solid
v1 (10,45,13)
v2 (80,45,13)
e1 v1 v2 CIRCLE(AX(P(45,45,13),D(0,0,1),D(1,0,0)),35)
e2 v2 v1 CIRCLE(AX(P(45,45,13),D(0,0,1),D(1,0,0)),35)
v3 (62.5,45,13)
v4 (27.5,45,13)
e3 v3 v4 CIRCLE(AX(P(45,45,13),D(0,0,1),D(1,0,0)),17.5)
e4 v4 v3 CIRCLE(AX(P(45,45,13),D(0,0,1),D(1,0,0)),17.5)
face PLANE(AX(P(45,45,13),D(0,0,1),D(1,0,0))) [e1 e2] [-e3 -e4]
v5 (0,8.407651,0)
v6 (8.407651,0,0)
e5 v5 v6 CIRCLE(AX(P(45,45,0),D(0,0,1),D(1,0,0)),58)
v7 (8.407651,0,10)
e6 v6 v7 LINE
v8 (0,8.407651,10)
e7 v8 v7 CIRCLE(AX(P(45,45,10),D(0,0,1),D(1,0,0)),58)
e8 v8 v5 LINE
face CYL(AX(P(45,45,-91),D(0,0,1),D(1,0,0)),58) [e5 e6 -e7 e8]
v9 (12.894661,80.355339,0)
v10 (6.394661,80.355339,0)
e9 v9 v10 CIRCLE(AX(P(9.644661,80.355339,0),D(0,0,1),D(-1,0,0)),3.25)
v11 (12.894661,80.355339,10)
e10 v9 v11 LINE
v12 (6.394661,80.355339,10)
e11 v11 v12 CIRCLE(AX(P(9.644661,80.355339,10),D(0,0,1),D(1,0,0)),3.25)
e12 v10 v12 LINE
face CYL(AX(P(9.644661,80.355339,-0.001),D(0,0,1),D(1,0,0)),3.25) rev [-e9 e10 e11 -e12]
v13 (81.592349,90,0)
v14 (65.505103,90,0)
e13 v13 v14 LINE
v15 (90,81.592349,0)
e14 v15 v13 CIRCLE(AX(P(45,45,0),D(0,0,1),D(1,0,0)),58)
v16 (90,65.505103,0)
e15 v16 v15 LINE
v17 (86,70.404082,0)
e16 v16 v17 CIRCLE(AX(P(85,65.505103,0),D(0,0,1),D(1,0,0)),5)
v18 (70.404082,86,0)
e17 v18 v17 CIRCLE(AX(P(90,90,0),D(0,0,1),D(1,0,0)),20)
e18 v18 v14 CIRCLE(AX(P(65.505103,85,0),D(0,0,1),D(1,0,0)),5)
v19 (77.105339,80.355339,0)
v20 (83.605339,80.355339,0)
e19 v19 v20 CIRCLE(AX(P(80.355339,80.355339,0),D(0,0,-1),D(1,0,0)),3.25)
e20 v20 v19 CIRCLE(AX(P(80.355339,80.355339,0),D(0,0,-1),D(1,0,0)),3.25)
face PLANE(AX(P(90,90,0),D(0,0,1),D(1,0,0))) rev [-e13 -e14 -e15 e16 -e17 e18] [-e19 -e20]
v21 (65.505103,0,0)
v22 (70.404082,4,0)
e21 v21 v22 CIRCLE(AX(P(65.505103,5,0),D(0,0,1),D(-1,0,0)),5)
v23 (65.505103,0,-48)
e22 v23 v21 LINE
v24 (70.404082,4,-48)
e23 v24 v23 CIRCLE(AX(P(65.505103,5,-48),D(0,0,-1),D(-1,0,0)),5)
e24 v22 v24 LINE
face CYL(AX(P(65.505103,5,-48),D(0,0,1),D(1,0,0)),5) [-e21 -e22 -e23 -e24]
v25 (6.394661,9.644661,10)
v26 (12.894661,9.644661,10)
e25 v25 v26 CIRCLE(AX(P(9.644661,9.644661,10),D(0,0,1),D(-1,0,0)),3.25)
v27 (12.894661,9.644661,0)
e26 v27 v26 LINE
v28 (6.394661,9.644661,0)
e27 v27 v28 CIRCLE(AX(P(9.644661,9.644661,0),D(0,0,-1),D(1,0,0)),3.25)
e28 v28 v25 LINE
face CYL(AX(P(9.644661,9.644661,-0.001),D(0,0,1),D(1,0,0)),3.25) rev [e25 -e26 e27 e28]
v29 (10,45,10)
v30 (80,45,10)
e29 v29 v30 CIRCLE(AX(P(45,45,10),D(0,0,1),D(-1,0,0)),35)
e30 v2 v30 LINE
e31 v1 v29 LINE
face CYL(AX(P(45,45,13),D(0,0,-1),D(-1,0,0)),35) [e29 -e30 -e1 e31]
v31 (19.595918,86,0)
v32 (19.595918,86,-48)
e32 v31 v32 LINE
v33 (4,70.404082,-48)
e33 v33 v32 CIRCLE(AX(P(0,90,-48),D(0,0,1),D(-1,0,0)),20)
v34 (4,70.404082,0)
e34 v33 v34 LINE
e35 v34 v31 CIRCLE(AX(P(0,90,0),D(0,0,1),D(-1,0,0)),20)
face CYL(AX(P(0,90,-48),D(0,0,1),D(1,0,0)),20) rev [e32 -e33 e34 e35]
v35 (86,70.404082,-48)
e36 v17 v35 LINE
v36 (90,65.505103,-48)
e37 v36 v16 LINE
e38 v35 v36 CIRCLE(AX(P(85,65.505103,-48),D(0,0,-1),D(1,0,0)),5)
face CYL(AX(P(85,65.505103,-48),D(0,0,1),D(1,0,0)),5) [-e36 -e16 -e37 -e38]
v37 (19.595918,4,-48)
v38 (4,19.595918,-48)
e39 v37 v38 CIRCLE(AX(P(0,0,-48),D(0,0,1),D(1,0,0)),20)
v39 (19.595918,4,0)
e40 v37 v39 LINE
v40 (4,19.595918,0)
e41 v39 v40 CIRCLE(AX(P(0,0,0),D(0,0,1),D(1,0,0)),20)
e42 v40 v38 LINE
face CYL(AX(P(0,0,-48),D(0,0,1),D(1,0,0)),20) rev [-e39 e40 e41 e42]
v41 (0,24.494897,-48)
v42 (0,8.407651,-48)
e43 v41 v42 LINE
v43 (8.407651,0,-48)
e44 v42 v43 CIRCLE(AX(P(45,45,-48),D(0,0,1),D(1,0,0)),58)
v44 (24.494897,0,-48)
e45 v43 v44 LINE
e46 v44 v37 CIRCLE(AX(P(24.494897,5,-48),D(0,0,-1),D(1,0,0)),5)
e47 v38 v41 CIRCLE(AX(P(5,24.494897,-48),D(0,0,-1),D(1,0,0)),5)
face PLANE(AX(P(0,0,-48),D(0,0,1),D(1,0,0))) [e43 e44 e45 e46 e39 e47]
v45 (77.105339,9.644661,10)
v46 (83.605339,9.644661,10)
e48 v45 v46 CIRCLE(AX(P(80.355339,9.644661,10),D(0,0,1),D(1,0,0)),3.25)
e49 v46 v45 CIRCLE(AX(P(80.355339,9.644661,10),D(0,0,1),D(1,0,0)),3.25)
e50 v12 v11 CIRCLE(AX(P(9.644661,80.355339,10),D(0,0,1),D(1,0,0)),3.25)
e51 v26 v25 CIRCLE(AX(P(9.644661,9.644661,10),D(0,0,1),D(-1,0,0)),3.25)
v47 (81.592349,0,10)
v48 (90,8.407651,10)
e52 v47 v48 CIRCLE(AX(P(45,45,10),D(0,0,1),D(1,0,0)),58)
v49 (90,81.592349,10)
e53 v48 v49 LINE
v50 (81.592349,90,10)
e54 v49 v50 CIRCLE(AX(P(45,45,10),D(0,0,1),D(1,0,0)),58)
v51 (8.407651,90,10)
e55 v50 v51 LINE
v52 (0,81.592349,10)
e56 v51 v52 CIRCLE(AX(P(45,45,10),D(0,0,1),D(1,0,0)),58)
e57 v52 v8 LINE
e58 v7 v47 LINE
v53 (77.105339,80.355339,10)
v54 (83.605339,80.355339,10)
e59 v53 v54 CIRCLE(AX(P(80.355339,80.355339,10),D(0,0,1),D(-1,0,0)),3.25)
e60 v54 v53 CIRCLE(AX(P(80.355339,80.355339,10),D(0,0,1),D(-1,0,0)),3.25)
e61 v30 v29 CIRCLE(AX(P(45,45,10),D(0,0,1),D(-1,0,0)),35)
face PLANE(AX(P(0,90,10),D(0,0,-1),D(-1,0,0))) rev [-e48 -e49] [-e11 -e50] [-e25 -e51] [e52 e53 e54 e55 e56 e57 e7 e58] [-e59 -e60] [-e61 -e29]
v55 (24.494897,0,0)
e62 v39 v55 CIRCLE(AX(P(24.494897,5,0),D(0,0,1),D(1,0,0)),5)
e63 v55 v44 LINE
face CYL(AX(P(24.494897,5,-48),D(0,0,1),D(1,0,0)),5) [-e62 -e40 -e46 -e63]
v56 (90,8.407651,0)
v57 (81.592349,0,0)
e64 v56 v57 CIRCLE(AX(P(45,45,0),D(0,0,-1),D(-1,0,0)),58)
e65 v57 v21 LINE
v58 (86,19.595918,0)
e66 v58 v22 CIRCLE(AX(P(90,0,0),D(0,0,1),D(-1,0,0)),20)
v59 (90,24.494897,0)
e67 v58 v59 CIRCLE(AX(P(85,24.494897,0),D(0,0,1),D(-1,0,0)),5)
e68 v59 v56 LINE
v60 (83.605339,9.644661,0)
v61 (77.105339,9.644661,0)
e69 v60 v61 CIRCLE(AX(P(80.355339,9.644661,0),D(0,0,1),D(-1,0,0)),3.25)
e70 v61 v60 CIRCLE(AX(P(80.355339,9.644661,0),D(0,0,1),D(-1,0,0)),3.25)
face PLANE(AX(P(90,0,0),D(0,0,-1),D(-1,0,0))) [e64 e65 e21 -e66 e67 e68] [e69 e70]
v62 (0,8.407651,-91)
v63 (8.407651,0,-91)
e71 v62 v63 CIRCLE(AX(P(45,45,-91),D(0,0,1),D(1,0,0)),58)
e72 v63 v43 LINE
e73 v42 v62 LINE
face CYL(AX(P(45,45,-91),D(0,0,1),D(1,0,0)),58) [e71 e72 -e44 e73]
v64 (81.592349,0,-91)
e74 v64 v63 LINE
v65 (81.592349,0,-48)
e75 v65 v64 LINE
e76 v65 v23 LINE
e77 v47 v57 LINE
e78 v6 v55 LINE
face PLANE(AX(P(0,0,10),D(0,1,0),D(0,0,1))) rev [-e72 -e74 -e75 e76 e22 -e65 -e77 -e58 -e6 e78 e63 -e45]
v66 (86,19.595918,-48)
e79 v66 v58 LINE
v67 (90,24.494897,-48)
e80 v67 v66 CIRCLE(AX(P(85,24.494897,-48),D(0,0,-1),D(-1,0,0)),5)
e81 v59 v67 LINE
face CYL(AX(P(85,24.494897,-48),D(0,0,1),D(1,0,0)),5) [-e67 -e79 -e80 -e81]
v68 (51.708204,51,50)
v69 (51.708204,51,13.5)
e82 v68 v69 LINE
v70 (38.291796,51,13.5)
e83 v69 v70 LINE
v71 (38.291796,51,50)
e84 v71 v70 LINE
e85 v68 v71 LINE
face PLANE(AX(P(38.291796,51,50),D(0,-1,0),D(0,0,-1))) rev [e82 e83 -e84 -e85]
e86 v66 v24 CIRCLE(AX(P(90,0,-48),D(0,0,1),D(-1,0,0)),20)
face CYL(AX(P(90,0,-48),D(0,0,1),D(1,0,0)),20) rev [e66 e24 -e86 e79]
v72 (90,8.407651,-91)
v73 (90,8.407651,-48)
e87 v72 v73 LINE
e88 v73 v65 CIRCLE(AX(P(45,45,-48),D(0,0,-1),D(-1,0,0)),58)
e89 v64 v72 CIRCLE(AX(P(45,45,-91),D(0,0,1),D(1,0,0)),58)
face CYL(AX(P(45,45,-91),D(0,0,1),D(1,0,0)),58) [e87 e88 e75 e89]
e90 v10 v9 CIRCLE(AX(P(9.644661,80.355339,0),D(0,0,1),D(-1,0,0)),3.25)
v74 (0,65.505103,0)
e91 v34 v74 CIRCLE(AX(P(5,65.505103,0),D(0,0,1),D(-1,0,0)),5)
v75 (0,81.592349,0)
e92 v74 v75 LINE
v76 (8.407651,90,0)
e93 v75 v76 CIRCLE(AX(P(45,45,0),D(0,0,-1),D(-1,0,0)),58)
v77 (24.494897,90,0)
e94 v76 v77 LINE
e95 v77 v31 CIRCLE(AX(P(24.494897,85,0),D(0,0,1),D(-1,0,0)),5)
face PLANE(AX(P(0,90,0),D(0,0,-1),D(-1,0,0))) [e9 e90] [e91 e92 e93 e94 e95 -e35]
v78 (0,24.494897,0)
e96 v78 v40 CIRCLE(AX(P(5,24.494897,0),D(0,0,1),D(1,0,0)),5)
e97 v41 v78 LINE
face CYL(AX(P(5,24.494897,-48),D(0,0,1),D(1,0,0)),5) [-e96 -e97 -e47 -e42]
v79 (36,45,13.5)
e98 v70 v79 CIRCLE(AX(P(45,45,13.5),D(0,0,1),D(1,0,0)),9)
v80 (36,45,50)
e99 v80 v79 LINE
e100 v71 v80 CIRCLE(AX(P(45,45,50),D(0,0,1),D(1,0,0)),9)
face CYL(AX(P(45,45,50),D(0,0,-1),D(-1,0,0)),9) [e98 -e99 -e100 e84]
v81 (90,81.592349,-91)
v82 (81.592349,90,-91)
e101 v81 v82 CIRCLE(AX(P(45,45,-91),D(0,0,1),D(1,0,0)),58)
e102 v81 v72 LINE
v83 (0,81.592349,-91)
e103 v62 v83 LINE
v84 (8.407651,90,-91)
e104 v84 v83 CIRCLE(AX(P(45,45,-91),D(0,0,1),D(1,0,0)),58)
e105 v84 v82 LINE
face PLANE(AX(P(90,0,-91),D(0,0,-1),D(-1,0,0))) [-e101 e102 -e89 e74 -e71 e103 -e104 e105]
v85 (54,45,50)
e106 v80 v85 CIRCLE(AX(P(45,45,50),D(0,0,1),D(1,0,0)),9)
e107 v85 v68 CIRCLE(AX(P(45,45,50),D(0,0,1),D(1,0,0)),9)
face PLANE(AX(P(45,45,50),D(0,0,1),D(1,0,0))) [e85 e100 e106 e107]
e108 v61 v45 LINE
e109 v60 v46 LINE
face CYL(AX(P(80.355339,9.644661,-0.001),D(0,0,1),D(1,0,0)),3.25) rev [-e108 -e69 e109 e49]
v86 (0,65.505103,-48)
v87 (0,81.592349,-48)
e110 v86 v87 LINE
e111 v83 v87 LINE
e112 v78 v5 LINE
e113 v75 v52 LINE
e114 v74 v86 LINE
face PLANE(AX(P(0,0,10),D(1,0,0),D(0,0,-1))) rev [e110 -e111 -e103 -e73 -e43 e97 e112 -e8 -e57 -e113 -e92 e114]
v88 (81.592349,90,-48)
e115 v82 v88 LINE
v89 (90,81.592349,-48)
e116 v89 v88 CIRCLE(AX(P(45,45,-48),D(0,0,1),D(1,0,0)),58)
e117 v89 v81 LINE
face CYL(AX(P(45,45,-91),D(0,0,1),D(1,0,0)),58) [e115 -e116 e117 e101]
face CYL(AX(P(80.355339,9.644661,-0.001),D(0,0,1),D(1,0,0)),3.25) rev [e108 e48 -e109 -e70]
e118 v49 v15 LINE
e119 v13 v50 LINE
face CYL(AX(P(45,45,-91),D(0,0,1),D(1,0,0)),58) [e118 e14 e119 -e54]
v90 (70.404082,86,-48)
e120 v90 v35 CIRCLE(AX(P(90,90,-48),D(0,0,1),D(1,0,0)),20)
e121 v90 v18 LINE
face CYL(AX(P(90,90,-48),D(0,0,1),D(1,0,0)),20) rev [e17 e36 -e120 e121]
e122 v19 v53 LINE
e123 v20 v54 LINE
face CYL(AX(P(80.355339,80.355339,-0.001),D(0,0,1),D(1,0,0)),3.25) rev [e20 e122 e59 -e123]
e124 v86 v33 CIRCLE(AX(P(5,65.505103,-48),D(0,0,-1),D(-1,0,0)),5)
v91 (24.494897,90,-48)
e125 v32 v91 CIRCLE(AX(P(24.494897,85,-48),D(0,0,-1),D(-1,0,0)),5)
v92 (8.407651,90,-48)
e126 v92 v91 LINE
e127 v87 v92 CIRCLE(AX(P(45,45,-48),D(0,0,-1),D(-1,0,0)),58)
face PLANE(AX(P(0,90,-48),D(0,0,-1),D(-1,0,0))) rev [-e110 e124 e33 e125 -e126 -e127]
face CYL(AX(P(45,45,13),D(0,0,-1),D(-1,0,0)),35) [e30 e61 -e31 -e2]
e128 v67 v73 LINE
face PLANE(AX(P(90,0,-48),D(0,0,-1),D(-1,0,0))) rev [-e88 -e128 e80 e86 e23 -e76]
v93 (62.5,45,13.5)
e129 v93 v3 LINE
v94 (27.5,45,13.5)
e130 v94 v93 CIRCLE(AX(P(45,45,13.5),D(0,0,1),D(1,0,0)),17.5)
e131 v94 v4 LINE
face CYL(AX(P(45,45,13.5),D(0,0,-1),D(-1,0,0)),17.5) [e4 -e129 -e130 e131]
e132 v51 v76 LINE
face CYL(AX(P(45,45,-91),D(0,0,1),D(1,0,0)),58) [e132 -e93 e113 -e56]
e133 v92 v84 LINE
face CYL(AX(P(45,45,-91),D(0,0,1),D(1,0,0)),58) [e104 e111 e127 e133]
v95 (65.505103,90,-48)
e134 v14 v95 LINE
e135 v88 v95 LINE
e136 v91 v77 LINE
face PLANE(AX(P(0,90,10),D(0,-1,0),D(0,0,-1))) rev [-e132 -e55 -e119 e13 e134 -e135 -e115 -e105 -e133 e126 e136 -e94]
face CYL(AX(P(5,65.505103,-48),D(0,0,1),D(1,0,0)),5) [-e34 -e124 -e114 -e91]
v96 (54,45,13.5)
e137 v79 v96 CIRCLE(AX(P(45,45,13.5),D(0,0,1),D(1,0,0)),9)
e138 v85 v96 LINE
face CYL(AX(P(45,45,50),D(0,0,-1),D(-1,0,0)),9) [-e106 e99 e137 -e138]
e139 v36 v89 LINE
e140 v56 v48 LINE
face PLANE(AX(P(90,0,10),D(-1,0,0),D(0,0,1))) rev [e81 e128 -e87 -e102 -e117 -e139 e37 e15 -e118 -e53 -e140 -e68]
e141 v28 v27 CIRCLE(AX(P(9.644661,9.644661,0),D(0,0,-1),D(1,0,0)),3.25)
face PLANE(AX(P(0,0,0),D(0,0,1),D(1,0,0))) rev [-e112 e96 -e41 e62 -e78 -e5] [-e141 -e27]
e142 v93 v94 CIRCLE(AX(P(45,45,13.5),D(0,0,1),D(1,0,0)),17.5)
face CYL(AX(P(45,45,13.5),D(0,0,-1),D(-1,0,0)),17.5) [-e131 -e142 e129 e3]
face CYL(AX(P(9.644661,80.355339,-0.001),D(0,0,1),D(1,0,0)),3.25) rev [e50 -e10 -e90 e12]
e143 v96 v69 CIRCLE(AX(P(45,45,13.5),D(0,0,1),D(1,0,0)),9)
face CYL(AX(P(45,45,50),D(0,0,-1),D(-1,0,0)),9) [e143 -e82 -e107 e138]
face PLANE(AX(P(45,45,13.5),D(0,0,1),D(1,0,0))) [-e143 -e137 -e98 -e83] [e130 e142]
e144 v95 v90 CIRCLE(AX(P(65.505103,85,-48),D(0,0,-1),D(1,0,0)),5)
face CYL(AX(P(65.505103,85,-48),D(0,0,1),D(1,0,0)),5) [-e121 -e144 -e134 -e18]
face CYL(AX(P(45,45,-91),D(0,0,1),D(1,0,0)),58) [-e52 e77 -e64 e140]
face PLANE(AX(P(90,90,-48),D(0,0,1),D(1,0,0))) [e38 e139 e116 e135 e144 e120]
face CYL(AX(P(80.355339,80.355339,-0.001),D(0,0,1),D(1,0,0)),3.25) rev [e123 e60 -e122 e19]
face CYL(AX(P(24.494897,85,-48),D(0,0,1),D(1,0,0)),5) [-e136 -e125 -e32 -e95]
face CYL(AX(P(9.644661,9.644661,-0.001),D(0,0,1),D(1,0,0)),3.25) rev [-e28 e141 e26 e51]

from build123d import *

# Parameters (mm, degrees)
SKETCH_1_W          = 90
SKETCH_1_H          = 90
EXTRUDE_1_DEPTH     = 10
SKETCH_2_R          = 35
EXTRUDE_2_DEPTH     = 3
SKETCH_3_R          = 17.5
EXTRUDE_3_DEPTH     = 0.5
EXTRUDE_4_DEPTH     = 36.5
CUT_EXTRUDE_1_REACH = 135.417
SKETCH_5_R          = 3.25
SKETCH_7_W          = 90
SKETCH_7_H          = 90
EXTRUDE_5_DEPTH     = 91
SKETCH_8_R          = 20
CUT_EXTRUDE_2_DEPTH = 48
FILLET_1_R          = 5
SKETCH_6_OUTSIDE_W  = 129.99
SKETCH_6_OUTSIDE_H  = 129.99
SKETCH_6_OUTSIDE_R  = 58
CUT_EXTRUDE_3_DEPTH = 163.483845351


with BuildPart() as part:
    # 草图1 → 拉伸1 (new body)
    with BuildSketch(Plane.XY):
        with Locations((45, 45)):
            Rectangle(SKETCH_1_W, SKETCH_1_H)
    extrude(amount=EXTRUDE_1_DEPTH)

    # 草图2 → 拉伸2 (add)
    with BuildSketch(Plane.XY.offset(10)):
        with Locations(Location((45, 45, 0), (0, 0, 180))):
            Circle(SKETCH_2_R)
    extrude(amount=EXTRUDE_2_DEPTH)

    # 草图3 → 拉伸3 (add)
    with BuildSketch(Plane.XY.offset(13)):
        with Locations((45, 45)):
            Circle(SKETCH_3_R)
    extrude(amount=EXTRUDE_3_DEPTH)

    # 草图4 → 拉伸4 (add)
    with BuildSketch(Plane.XY.offset(13.5)):
        with BuildLine():
            Line((38.291796068, 51), (51.708203932, 51))
            ThreePointArc((51.708203932, 51), (45, 36), (38.291796068, 51))
        make_face()
    extrude(amount=EXTRUDE_4_DEPTH)

    # 草图5 → 切除-拉伸1 (cut, up to next)
    with BuildSketch(Plane.XY.offset(10), mode=Mode.PRIVATE) as cut_extrude_1_sk1:
        with Locations((9.644660941, 80.355339059)):
            Circle(SKETCH_5_R)
    cut_extrude_1_tool1 = extrude(cut_extrude_1_sk1.sketch, amount=-CUT_EXTRUDE_1_REACH, mode=Mode.PRIVATE) & part.part
    # 草图5 → 切除-拉伸1 (cut, up to next)
    with BuildSketch(Plane.XY.offset(10), mode=Mode.PRIVATE) as cut_extrude_1_sk2:
        with Locations(Location((80.355339059, 80.355339059, 0), (0, 0, 180))):
            Circle(SKETCH_5_R)
    cut_extrude_1_tool2 = extrude(cut_extrude_1_sk2.sketch, amount=-CUT_EXTRUDE_1_REACH, mode=Mode.PRIVATE) & part.part
    # 草图5 → 切除-拉伸1 (cut, up to next)
    with BuildSketch(Plane.XY.offset(10), mode=Mode.PRIVATE) as cut_extrude_1_sk3:
        with Locations((80.355339059, 9.644660941)):
            Circle(SKETCH_5_R)
    cut_extrude_1_tool3 = extrude(cut_extrude_1_sk3.sketch, amount=-CUT_EXTRUDE_1_REACH, mode=Mode.PRIVATE) & part.part
    # 草图5 → 切除-拉伸1 (cut, up to next)
    with BuildSketch(Plane.XY.offset(10), mode=Mode.PRIVATE) as cut_extrude_1_sk4:
        with Locations(Location((9.644660941, 9.644660941, 0), (0, 0, 180))):
            Circle(SKETCH_5_R)
    cut_extrude_1_tool4 = extrude(cut_extrude_1_sk4.sketch, amount=-CUT_EXTRUDE_1_REACH, mode=Mode.PRIVATE) & part.part
    add(cut_extrude_1_tool1.solids().sort_by_distance((9.644661, 80.355339, 10))[0], mode=Mode.SUBTRACT)
    add(cut_extrude_1_tool2.solids().sort_by_distance((80.355339, 80.355339, 10))[0], mode=Mode.SUBTRACT)
    add(cut_extrude_1_tool3.solids().sort_by_distance((80.355339, 9.644661, 10))[0], mode=Mode.SUBTRACT)
    add(cut_extrude_1_tool4.solids().sort_by_distance((9.644661, 9.644661, 10))[0], mode=Mode.SUBTRACT)

    # 草图7 → 拉伸5 (add)
    with BuildSketch(Plane(origin=(0, 0, 0), x_dir=(-1, 0, 0), z_dir=(0, 0, -1))):
        with Locations((-45, 45)):
            Rectangle(SKETCH_7_W, SKETCH_7_H)
    extrude(amount=EXTRUDE_5_DEPTH)

    # 草图8 → 切除-拉伸2 (cut)
    with BuildSketch(Plane.XY):
        with Locations((90, 90)):
            Circle(SKETCH_8_R)
        with Locations((90, 0)):
            Circle(SKETCH_8_R)
        Circle(SKETCH_8_R)
        with Locations((0, 90)):
            Circle(SKETCH_8_R)
    extrude(amount=-CUT_EXTRUDE_2_DEPTH, mode=Mode.SUBTRACT)

    # 圆角1
    fillet_1_edges = [part.edges().sort_by_distance(p)[0] for p in [
        (70, 90, -24),
        (90, 70, -24),
        (70, 0, -24),
        (90, 20, -24),
        (20, 0, -24),
        (0, 20, -24),
        (20, 90, -24),
        (0, 70, -24),
    ]]
    fillet(fillet_1_edges, radius=FILLET_1_R)

    # 草图6 outside → 切除-拉伸3 (cut, through all)
    with BuildSketch(Plane.XY.offset(10)):
        with Locations((45, 45)):
            Rectangle(SKETCH_6_OUTSIDE_W, SKETCH_6_OUTSIDE_H)
        with Locations((45, 45)):
            Circle(SKETCH_6_OUTSIDE_R, mode=Mode.SUBTRACT)
    extrude(amount=-CUT_EXTRUDE_3_DEPTH, mode=Mode.SUBTRACT)


solid = part.part
